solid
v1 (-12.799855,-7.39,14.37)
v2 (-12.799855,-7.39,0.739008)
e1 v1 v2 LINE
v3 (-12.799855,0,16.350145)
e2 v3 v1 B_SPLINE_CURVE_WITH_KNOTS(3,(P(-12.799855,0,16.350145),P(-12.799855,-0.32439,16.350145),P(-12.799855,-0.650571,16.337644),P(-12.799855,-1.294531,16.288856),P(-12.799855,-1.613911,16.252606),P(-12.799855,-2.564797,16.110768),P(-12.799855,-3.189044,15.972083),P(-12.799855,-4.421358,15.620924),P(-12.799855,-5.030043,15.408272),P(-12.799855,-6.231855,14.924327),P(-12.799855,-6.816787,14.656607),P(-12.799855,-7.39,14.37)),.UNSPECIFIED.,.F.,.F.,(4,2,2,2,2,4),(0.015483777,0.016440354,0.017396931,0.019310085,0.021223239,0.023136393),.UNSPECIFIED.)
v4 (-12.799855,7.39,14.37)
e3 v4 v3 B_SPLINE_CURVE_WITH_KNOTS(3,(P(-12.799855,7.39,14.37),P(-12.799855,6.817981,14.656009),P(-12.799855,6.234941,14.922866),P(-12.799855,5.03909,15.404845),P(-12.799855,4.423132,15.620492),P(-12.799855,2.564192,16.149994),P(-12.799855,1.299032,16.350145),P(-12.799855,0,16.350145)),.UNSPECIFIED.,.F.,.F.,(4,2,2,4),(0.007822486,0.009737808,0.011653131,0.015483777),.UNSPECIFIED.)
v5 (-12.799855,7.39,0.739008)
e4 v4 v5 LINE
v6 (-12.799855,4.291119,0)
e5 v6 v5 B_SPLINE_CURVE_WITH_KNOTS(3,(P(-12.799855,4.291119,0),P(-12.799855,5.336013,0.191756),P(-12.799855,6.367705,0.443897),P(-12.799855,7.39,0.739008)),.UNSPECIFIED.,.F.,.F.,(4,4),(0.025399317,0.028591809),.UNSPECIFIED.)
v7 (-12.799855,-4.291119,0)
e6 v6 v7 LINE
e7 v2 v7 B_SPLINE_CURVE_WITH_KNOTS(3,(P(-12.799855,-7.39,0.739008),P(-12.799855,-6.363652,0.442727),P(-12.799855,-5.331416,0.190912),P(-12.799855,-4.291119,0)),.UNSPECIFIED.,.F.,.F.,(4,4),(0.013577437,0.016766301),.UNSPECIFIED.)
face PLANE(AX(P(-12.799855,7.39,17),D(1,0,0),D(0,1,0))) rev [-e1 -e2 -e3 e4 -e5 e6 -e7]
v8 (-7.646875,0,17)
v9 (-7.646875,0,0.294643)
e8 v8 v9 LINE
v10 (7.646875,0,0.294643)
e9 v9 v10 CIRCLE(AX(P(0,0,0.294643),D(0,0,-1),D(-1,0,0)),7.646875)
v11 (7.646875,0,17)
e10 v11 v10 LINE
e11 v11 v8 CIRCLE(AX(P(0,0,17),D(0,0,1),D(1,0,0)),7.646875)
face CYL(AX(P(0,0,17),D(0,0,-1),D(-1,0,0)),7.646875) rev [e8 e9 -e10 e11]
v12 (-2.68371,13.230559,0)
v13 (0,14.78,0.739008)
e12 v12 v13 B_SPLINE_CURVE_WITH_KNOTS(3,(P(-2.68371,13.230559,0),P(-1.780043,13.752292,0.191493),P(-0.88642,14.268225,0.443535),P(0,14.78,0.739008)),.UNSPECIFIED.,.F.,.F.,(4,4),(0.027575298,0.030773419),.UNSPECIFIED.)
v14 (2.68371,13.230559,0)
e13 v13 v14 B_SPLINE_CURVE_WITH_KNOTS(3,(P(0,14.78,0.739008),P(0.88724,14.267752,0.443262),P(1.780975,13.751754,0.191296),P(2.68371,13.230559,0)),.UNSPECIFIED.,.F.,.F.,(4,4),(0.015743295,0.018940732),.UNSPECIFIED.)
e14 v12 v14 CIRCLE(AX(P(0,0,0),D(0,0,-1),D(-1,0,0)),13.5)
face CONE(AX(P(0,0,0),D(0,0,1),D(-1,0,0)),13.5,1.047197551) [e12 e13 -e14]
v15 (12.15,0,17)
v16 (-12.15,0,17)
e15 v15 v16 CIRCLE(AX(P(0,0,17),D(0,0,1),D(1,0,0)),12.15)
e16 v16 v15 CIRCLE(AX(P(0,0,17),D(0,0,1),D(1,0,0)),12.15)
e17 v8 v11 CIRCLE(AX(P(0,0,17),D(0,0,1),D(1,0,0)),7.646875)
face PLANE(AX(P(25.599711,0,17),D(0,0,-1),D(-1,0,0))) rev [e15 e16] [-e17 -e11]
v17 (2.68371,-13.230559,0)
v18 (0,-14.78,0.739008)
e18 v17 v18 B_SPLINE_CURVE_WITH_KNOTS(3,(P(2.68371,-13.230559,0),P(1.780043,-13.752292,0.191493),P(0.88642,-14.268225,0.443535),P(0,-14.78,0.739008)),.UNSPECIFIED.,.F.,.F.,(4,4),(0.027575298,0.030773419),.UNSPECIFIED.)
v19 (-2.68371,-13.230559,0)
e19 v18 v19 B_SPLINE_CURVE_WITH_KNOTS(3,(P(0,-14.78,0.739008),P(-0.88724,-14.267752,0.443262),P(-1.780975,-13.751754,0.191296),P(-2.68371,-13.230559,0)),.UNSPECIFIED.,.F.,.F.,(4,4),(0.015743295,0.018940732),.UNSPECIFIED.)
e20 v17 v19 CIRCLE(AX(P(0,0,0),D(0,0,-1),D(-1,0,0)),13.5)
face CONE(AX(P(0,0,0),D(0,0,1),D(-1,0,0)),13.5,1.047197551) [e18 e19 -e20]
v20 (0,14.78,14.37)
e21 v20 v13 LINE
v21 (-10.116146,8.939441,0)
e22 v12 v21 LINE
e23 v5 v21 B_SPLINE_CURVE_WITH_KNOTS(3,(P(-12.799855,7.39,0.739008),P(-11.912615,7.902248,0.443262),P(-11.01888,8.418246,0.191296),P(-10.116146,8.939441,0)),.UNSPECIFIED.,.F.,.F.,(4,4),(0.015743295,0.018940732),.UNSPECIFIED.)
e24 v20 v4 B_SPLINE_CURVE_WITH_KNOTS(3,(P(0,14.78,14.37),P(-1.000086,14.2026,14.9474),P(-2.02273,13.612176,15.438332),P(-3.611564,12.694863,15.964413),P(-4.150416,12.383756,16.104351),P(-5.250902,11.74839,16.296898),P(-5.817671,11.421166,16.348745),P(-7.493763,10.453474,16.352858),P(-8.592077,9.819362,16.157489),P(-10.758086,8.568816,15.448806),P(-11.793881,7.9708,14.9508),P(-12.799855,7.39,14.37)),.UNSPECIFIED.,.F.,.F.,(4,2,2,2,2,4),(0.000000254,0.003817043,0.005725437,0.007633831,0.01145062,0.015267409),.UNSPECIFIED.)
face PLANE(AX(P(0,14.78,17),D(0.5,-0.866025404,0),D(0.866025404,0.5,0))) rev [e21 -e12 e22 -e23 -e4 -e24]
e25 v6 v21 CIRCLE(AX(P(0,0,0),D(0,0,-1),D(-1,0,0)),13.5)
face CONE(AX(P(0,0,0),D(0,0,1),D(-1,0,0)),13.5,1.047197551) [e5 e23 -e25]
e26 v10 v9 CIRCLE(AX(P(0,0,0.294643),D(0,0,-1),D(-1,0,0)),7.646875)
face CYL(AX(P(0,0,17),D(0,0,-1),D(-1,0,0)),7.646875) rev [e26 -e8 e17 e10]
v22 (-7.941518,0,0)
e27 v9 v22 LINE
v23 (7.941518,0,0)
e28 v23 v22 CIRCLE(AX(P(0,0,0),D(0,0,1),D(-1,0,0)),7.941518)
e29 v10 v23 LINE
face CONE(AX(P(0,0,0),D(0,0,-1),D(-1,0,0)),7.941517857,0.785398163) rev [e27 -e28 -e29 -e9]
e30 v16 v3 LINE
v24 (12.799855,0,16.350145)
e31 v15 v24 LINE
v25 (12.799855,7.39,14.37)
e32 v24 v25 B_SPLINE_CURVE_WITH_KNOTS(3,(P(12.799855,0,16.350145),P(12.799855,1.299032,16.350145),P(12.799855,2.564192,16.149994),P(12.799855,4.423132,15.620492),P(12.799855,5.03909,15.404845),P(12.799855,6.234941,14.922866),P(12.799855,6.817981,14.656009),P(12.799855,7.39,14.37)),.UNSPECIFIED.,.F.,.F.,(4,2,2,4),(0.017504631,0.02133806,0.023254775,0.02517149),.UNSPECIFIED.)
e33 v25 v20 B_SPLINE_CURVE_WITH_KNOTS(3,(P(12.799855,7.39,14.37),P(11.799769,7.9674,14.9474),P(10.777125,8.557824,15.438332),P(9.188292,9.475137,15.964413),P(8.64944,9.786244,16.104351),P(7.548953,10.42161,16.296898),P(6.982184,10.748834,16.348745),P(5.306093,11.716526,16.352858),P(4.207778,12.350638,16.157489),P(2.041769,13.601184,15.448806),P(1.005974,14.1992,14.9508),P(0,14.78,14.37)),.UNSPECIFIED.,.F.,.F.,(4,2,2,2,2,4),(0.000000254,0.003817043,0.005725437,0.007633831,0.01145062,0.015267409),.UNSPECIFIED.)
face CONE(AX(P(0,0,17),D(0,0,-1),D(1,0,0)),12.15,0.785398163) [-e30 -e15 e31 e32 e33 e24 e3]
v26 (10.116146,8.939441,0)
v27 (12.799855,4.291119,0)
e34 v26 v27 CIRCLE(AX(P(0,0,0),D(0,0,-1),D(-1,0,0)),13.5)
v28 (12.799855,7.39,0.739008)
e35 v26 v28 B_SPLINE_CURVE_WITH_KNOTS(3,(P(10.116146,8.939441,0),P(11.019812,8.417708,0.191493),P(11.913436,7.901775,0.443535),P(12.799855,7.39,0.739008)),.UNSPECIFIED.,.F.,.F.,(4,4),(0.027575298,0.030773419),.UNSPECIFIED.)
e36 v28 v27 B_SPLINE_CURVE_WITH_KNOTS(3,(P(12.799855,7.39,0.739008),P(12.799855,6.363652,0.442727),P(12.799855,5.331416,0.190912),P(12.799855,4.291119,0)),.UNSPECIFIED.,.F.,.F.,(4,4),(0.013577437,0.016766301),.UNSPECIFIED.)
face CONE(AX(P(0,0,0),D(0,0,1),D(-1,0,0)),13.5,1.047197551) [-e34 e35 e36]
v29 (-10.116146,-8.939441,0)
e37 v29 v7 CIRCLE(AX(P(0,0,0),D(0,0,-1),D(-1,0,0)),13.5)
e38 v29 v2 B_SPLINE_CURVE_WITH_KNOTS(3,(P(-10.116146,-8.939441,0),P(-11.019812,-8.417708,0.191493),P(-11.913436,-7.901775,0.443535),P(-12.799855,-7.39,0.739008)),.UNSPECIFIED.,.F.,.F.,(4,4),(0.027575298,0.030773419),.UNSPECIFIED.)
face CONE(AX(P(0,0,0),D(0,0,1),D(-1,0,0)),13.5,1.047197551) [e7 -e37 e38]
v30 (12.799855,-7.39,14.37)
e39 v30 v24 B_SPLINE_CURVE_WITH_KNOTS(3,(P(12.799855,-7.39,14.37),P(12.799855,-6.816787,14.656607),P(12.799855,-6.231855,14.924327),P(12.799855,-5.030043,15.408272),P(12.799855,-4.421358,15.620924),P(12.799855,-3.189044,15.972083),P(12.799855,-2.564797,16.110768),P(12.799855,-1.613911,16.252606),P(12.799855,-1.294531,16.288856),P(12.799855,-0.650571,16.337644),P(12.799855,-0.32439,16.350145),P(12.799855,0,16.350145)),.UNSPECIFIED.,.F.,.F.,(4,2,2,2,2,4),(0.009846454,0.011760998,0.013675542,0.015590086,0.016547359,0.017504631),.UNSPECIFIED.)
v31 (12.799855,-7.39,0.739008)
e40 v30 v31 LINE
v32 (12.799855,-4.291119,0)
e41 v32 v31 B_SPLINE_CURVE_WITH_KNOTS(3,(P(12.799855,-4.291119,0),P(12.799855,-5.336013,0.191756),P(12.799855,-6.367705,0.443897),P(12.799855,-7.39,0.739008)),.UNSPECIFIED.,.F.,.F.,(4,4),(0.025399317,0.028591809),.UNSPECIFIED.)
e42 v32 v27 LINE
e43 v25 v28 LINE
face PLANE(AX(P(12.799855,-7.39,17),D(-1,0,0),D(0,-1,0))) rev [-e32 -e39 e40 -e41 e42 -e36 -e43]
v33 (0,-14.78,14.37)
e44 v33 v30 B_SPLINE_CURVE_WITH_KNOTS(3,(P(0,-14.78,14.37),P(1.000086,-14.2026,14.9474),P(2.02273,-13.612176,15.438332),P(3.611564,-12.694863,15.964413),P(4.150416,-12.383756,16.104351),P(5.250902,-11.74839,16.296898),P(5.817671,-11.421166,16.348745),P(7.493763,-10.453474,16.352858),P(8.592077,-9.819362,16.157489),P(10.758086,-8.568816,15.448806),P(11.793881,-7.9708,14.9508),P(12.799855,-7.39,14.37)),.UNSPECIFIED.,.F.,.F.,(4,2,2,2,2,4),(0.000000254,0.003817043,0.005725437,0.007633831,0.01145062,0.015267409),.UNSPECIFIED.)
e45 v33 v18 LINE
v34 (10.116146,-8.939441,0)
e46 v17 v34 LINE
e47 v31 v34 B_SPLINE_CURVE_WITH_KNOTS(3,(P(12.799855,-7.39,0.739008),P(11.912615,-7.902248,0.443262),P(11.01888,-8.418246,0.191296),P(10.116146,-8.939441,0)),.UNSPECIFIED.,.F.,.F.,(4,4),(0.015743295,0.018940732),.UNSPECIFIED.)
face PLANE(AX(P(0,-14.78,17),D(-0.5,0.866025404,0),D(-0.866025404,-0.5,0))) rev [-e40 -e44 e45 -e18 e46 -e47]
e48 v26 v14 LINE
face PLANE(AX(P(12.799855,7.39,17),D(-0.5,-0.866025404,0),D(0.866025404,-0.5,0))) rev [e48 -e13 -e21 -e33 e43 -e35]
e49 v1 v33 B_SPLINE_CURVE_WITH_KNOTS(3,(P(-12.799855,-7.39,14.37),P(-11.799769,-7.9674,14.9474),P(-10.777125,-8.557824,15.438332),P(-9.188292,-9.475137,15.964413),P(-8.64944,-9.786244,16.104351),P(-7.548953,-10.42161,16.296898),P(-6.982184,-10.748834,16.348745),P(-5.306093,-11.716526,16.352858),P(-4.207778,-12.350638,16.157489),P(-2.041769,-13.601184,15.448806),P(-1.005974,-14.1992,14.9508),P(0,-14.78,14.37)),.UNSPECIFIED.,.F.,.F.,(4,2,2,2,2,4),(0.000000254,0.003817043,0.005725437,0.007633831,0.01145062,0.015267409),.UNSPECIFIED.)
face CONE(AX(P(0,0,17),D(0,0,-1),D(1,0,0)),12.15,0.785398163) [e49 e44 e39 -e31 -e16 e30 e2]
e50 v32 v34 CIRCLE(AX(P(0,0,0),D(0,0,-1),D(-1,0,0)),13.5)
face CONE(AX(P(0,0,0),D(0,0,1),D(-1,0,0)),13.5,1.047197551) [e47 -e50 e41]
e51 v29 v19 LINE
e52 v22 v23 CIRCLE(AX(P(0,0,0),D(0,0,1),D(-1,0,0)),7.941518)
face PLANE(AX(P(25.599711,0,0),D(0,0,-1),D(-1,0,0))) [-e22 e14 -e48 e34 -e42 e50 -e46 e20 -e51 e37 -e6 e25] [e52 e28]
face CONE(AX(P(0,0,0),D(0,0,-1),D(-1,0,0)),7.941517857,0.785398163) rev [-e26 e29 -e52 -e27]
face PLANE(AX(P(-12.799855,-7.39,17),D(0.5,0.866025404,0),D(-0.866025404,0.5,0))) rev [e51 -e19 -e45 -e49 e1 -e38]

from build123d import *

# Parameters (mm, degrees)
SKETCH_1_R          = 7.646875
EXTRUDE_555_DEPTH   = 17
SKETCH_2_OUTSIDE_W  = 129.344
SKETCH_2_OUTSIDE_H  = 133.304
SKETCH_2_OUTSIDE_R  = 13.5
CUT_EXTRUDE_1_DEPTH = 26.909162472
CUT_EXTRUDE_1_DRAFT = -60
CHAMFER_1_SIZE      = 0.294642857
SKETCH_9_OUTSIDE_W  = 89.946
SKETCH_9_OUTSIDE_H  = 93.906
SKETCH_9_OUTSIDE_R  = 12.15
CUT_EXTRUDE_7_DEPTH = 26.909162472
CUT_EXTRUDE_7_DRAFT = -45


with BuildPart() as part:
    # 草图1 → Extrude 555 (new body)
    with BuildSketch(Plane.XY):
        Polygon((0, 14.78), (-12.799855468, 7.39), (-12.799855468, -7.39), (0, -14.78), (12.799855468, -7.39), (12.799855468, 7.39), align=None)
        Circle(SKETCH_1_R, mode=Mode.SUBTRACT)
    extrude(amount=EXTRUDE_555_DEPTH)


with BuildPart() as cut_extrude_1_tool:
    # 草图2 outside → 切除-拉伸1 (with draft: the straight prism first)
    with BuildSketch(Plane(origin=(0, 0, 0), x_dir=(-1, 0, 0), z_dir=(0, 0, -1))):
        Rectangle(SKETCH_2_OUTSIDE_W, SKETCH_2_OUTSIDE_H)
        Circle(SKETCH_2_OUTSIDE_R, mode=Mode.SUBTRACT)
    extrude(amount=-CUT_EXTRUDE_1_DEPTH)
    # 切除-拉伸1: the draft: its side faces are tilted about the plane it starts from
    cut_extrude_1_sides = [cut_extrude_1_tool.faces().sort_by_distance(p)[0] for p in [
        (0, -66.652, 13.454581236),
        (-64.672, 0, 13.454581236),
        (0, 66.652, 13.454581236),
        (64.672, 0, 13.454581236),
        (13.5, 0, 13.454581236),
    ]]
    draft(cut_extrude_1_sides, Plane(origin=(0, 0, 0), x_dir=(-1, 0, 0), z_dir=(0, 0, -1)), CUT_EXTRUDE_1_DRAFT)


with BuildPart() as part_1:
    add(part.part)

    # 切除-拉伸1: cut by cut_extrude_1_tool
    add(cut_extrude_1_tool.part, mode=Mode.SUBTRACT)

    # 倒角1
    chamfer_1_edges = [part_1.edges().sort_by_distance(p)[0] for p in [
        (-7.646875, 0, 0),
    ]]
    chamfer(chamfer_1_edges, length=CHAMFER_1_SIZE)


with BuildPart() as cut_extrude_7_tool:
    # 草图9 outside → 切除-拉伸7 (with draft: the straight prism first)
    with BuildSketch(Plane.XY.offset(17)):
        Rectangle(SKETCH_9_OUTSIDE_W, SKETCH_9_OUTSIDE_H)
        Circle(SKETCH_9_OUTSIDE_R, mode=Mode.SUBTRACT)
    extrude(amount=-CUT_EXTRUDE_7_DEPTH)
    # 切除-拉伸7: the draft: its side faces are tilted about the plane it starts from
    cut_extrude_7_sides = [cut_extrude_7_tool.faces().sort_by_distance(p)[0] for p in [
        (0, -46.953, 3.545418764),
        (44.973, 0, 3.545418764),
        (0, 46.953, 3.545418764),
        (-44.973, 0, 3.545418764),
        (-12.15, 0, 3.545418764),
    ]]
    draft(cut_extrude_7_sides, Plane.XY.offset(17), CUT_EXTRUDE_7_DRAFT)


with BuildPart() as part_2:
    add(part_1.part)

    # 切除-拉伸7: cut by cut_extrude_7_tool
    add(cut_extrude_7_tool.part, mode=Mode.SUBTRACT)


solid = part_2.part
